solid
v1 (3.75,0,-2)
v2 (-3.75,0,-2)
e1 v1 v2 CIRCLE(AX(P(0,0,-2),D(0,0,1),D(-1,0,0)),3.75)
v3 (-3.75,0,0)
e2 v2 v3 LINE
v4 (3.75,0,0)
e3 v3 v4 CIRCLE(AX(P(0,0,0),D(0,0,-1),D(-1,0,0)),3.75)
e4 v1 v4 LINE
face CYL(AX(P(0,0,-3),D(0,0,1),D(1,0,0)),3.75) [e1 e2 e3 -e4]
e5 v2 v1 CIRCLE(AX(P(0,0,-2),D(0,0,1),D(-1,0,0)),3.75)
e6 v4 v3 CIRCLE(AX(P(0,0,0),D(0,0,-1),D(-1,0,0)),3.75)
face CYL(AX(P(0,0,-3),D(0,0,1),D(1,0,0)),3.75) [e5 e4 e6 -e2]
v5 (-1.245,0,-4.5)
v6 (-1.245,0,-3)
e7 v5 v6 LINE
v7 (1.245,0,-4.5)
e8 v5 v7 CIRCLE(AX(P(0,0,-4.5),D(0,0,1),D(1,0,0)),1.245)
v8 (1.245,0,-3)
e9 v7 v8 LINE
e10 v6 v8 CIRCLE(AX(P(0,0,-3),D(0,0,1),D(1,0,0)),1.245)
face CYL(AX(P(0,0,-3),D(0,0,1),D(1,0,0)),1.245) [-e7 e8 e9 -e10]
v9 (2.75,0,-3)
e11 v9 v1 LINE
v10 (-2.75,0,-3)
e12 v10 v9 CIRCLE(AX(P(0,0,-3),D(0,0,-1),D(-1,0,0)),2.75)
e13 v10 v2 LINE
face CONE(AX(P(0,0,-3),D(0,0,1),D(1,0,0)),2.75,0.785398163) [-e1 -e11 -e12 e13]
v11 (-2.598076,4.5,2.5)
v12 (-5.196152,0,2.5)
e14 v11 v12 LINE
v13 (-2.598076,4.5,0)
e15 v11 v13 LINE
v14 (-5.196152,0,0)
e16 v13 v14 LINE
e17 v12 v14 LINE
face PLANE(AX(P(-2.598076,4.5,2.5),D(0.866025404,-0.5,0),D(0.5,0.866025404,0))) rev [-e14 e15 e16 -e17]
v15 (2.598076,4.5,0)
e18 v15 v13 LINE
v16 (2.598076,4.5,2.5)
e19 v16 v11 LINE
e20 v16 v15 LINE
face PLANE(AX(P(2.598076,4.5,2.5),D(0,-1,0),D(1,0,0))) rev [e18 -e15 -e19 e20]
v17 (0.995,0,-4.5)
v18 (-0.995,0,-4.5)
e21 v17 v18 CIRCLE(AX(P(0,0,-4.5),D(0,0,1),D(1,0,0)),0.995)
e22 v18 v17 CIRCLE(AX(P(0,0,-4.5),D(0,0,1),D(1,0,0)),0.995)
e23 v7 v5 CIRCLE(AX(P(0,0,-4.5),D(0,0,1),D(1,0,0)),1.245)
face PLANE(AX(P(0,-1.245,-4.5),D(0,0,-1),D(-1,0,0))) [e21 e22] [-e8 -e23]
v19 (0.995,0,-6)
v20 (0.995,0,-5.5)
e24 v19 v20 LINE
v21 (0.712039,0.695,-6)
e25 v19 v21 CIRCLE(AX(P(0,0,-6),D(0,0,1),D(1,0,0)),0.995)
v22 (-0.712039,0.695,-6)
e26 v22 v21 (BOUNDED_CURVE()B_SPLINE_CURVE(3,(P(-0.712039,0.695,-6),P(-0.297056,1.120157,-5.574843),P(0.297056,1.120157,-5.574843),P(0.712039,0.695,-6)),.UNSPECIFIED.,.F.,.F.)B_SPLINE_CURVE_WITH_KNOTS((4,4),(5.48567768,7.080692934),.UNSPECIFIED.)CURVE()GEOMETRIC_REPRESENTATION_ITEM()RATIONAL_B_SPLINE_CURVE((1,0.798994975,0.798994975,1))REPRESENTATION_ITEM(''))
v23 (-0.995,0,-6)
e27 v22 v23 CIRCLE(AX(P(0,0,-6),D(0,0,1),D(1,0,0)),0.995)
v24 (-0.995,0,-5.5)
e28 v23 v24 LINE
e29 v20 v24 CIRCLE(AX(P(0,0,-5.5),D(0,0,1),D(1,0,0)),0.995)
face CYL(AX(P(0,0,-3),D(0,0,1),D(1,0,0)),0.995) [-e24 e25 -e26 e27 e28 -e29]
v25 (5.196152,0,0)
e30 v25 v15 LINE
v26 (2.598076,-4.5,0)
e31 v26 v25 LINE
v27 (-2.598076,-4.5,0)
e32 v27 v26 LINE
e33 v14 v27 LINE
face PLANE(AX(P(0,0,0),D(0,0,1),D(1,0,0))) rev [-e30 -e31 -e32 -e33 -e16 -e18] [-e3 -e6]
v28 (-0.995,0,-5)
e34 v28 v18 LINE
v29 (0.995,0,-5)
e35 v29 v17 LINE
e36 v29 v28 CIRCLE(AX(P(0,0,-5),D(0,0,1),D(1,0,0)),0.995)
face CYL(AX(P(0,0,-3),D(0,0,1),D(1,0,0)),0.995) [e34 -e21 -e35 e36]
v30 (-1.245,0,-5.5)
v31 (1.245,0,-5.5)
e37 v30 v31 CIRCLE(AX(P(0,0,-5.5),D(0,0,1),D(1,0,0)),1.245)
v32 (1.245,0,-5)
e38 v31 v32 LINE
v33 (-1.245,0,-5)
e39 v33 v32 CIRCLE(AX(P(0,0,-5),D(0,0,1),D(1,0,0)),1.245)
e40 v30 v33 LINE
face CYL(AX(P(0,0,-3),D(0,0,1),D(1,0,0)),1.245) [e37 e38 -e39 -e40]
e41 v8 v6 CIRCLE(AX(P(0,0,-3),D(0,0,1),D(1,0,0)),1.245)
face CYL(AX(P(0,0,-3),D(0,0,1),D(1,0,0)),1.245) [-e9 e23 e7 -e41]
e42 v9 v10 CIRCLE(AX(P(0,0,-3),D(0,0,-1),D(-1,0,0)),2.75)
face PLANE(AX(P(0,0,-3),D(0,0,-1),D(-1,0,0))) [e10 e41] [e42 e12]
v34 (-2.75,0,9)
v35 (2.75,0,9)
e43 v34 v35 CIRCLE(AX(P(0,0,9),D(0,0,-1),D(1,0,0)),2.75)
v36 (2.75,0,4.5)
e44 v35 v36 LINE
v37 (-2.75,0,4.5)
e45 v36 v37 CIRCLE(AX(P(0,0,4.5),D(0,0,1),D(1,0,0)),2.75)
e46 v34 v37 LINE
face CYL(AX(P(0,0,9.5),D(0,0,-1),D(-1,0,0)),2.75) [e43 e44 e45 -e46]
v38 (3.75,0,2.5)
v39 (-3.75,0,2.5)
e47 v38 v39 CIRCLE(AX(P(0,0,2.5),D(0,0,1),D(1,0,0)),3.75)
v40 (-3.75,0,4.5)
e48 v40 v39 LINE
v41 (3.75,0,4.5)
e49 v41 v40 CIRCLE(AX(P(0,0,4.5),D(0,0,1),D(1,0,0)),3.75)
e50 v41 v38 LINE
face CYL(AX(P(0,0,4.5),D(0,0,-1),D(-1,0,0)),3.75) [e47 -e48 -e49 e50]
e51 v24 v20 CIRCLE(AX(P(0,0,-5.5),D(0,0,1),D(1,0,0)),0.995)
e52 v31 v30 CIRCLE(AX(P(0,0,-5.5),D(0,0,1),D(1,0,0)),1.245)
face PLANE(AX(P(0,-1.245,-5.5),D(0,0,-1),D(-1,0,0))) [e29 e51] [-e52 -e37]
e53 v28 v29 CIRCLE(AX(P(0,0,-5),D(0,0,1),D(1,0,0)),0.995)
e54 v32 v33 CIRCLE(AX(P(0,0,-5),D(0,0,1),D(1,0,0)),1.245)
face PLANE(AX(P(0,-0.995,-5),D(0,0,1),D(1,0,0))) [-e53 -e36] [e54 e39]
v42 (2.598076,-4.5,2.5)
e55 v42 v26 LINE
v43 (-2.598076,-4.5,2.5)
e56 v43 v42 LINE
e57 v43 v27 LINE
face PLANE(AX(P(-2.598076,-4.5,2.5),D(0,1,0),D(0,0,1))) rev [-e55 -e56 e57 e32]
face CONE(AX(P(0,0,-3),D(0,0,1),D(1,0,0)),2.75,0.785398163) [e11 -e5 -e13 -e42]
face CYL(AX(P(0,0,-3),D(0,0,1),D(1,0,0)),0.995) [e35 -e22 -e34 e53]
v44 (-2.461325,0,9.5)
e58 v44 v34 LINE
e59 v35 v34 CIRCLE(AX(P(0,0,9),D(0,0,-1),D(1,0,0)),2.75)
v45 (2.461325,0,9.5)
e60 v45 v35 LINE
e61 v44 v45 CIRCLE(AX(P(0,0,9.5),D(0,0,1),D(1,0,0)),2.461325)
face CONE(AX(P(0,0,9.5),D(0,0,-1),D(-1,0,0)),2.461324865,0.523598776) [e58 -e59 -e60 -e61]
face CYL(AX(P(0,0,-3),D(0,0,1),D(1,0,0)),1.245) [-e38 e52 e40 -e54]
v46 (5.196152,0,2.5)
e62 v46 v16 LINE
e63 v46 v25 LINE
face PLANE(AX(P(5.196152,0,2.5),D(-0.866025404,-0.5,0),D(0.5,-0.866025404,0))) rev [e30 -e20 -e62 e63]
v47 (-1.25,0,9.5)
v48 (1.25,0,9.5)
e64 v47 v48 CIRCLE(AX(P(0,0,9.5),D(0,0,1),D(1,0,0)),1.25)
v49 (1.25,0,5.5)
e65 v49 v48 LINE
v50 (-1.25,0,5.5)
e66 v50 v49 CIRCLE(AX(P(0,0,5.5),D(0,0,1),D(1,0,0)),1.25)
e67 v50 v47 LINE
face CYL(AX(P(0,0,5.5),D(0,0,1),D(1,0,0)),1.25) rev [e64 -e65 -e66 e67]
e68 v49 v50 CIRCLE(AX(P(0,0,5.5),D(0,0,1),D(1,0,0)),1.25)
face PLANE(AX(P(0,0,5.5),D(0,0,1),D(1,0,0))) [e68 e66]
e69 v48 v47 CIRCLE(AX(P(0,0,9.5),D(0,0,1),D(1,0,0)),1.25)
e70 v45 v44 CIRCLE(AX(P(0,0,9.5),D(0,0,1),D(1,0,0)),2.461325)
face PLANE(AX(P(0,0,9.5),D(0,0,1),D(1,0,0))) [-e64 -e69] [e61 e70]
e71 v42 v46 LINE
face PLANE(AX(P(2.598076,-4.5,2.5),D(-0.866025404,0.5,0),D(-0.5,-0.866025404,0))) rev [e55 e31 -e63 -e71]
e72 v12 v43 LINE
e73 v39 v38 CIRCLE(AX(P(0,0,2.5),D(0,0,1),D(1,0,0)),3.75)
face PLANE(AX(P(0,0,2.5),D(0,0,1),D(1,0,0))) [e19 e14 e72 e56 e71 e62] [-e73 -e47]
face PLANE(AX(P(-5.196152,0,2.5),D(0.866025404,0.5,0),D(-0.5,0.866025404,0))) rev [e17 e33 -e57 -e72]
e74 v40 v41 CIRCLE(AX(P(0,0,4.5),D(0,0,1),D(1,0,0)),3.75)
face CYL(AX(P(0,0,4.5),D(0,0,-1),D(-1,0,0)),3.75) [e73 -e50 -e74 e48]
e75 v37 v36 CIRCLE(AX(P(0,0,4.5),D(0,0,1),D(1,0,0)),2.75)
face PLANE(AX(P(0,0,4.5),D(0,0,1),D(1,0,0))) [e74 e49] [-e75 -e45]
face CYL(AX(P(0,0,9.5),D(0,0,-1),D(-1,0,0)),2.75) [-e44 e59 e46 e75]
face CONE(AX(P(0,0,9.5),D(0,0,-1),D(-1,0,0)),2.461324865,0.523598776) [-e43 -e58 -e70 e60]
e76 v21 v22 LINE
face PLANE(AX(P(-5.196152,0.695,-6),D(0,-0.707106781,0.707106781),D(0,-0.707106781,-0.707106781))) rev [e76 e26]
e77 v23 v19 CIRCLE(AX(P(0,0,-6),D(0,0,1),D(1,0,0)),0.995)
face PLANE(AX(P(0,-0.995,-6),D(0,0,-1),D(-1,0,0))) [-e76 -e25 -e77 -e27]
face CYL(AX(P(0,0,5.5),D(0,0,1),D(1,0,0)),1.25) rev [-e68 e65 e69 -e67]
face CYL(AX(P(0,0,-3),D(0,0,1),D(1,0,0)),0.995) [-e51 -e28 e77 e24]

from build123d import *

# Parameters (mm, degrees)
HEX_BODY_9AF_DEPTH            = 2.5
COLLAR_7_5_SKETCH_R           = 3.75
COLLAR_7_5_DEPTH              = 2
TIP_BODY_5_5_SKETCH_R         = 2.75
TIP_BODY_5_5_DEPTH            = 5
TIP_END_CHAMFER_0_5X30_SIZE   = 0.5
TIP_END_CHAMFER_0_5X30_SIZE2  = 0.288675135
TIP_BORE_2_5_SKETCH_R         = 1.25
TIP_BORE_2_5_DEPTH            = 4
SHANK_START                   = 3
SHANK_7_5_SKETCH_R            = 3.75
SHANK_7_5_DEPTH               = 3
SHANK_CHAMFER_1X45_SIZE       = 1
TERMINAL_NOTCH_CUT_DEPTH      = 12.7260394
TERMINAL_NOTCH_CUT_DEPTH_BACK = 12.7260394


with BuildPart() as part:
    # Hex Profile 9AF Sketch → Hex Body 9AF (new body)
    with BuildSketch(Plane.XY):
        Polygon((2.598076211, 4.5), (-2.598076211, 4.5), (-5.196152423, 0), (-2.598076211, -4.5), (2.598076211, -4.5), (5.196152423, 0), align=None)
    extrude(amount=HEX_BODY_9AF_DEPTH)

    # Collar Ø7.5 Sketch → Collar Ø7.5 (add)
    with BuildSketch(Plane.XY.offset(2.5)):
        Circle(COLLAR_7_5_SKETCH_R)
    extrude(amount=COLLAR_7_5_DEPTH)

    # Tip Body Ø5.5 Sketch → Tip Body Ø5.5 (add)
    with BuildSketch(Plane.XY.offset(4.5)):
        Circle(TIP_BODY_5_5_SKETCH_R)
    extrude(amount=TIP_BODY_5_5_DEPTH)

    # Tip End Chamfer 0.5x30
    tip_end_chamfer_0_5x30_edges = [part.edges().sort_by_distance(p)[0] for p in [
        (-2.75, 0, 9.5),
    ]]
    tip_end_chamfer_0_5x30_side = [part.faces().sort_by_distance(p)[0] for p in [
        (-2.75, 0, 7),
    ]]
    chamfer(tip_end_chamfer_0_5x30_edges, length=TIP_END_CHAMFER_0_5X30_SIZE, length2=TIP_END_CHAMFER_0_5X30_SIZE2, reference=tip_end_chamfer_0_5x30_side[0])

    # Tip Bore Ø2.5 Sketch → Tip Bore Ø2.5 (cut)
    with BuildSketch(Plane.XY.offset(9.5)):
        Circle(TIP_BORE_2_5_SKETCH_R)
    extrude(amount=-TIP_BORE_2_5_DEPTH, mode=Mode.SUBTRACT)

    # Shank Ø7.5 Sketch → Shank Ø7.5 (add)
    with BuildSketch(Plane(origin=(0, 0, 0), x_dir=(-1, 0, 0), z_dir=(0, 0, -1)).offset(SHANK_START)):
        with Locations(Location((0, 0, 0), (0, 0, 180))):
            Circle(SHANK_7_5_SKETCH_R)
    extrude(amount=-SHANK_7_5_DEPTH)

    # Shank Chamfer 1x45
    shank_chamfer_1x45_edges = [part.edges().sort_by_distance(p)[0] for p in [
        (-3.75, 0, -3),
    ]]
    chamfer(shank_chamfer_1x45_edges, length=SHANK_CHAMFER_1X45_SIZE)

    # Terminal Stud Profile Sketch → Terminal Stud (revolve)
    with BuildSketch(Plane(origin=(0, 0, 0), x_dir=(0, 0, -1), z_dir=(1, 0, 0)), mode=Mode.PRIVATE) as terminal_stud_sk:
        Polygon((3, -1.245), (4.5, -1.245), (4.5, -0.995), (5, -0.995), (5, -1.245), (5.5, -1.245), (5.5, -0.995), (6, -0.995), (6, 0), (3, 0), align=None)
    revolve(terminal_stud_sk.sketch.rotate(Axis((0, 0, -3), (0, 0, -1)), 270), axis=Axis((0, 0, -3), (0, 0, -1)))

    # Terminal Notch Sketch → Terminal Notch Cut (cut, two sides: drawn at the far end of the back side and taken through both)
    with BuildSketch(Plane(origin=(0, 0, 0), x_dir=(0, 0, -1), z_dir=(1, 0, 0)).offset(-TERMINAL_NOTCH_CUT_DEPTH_BACK)):
        Polygon((6, 0.695), (5.7, 0.995), (6, 0.995), align=None)
    extrude(amount=TERMINAL_NOTCH_CUT_DEPTH + TERMINAL_NOTCH_CUT_DEPTH_BACK, mode=Mode.SUBTRACT)


solid = part.part
